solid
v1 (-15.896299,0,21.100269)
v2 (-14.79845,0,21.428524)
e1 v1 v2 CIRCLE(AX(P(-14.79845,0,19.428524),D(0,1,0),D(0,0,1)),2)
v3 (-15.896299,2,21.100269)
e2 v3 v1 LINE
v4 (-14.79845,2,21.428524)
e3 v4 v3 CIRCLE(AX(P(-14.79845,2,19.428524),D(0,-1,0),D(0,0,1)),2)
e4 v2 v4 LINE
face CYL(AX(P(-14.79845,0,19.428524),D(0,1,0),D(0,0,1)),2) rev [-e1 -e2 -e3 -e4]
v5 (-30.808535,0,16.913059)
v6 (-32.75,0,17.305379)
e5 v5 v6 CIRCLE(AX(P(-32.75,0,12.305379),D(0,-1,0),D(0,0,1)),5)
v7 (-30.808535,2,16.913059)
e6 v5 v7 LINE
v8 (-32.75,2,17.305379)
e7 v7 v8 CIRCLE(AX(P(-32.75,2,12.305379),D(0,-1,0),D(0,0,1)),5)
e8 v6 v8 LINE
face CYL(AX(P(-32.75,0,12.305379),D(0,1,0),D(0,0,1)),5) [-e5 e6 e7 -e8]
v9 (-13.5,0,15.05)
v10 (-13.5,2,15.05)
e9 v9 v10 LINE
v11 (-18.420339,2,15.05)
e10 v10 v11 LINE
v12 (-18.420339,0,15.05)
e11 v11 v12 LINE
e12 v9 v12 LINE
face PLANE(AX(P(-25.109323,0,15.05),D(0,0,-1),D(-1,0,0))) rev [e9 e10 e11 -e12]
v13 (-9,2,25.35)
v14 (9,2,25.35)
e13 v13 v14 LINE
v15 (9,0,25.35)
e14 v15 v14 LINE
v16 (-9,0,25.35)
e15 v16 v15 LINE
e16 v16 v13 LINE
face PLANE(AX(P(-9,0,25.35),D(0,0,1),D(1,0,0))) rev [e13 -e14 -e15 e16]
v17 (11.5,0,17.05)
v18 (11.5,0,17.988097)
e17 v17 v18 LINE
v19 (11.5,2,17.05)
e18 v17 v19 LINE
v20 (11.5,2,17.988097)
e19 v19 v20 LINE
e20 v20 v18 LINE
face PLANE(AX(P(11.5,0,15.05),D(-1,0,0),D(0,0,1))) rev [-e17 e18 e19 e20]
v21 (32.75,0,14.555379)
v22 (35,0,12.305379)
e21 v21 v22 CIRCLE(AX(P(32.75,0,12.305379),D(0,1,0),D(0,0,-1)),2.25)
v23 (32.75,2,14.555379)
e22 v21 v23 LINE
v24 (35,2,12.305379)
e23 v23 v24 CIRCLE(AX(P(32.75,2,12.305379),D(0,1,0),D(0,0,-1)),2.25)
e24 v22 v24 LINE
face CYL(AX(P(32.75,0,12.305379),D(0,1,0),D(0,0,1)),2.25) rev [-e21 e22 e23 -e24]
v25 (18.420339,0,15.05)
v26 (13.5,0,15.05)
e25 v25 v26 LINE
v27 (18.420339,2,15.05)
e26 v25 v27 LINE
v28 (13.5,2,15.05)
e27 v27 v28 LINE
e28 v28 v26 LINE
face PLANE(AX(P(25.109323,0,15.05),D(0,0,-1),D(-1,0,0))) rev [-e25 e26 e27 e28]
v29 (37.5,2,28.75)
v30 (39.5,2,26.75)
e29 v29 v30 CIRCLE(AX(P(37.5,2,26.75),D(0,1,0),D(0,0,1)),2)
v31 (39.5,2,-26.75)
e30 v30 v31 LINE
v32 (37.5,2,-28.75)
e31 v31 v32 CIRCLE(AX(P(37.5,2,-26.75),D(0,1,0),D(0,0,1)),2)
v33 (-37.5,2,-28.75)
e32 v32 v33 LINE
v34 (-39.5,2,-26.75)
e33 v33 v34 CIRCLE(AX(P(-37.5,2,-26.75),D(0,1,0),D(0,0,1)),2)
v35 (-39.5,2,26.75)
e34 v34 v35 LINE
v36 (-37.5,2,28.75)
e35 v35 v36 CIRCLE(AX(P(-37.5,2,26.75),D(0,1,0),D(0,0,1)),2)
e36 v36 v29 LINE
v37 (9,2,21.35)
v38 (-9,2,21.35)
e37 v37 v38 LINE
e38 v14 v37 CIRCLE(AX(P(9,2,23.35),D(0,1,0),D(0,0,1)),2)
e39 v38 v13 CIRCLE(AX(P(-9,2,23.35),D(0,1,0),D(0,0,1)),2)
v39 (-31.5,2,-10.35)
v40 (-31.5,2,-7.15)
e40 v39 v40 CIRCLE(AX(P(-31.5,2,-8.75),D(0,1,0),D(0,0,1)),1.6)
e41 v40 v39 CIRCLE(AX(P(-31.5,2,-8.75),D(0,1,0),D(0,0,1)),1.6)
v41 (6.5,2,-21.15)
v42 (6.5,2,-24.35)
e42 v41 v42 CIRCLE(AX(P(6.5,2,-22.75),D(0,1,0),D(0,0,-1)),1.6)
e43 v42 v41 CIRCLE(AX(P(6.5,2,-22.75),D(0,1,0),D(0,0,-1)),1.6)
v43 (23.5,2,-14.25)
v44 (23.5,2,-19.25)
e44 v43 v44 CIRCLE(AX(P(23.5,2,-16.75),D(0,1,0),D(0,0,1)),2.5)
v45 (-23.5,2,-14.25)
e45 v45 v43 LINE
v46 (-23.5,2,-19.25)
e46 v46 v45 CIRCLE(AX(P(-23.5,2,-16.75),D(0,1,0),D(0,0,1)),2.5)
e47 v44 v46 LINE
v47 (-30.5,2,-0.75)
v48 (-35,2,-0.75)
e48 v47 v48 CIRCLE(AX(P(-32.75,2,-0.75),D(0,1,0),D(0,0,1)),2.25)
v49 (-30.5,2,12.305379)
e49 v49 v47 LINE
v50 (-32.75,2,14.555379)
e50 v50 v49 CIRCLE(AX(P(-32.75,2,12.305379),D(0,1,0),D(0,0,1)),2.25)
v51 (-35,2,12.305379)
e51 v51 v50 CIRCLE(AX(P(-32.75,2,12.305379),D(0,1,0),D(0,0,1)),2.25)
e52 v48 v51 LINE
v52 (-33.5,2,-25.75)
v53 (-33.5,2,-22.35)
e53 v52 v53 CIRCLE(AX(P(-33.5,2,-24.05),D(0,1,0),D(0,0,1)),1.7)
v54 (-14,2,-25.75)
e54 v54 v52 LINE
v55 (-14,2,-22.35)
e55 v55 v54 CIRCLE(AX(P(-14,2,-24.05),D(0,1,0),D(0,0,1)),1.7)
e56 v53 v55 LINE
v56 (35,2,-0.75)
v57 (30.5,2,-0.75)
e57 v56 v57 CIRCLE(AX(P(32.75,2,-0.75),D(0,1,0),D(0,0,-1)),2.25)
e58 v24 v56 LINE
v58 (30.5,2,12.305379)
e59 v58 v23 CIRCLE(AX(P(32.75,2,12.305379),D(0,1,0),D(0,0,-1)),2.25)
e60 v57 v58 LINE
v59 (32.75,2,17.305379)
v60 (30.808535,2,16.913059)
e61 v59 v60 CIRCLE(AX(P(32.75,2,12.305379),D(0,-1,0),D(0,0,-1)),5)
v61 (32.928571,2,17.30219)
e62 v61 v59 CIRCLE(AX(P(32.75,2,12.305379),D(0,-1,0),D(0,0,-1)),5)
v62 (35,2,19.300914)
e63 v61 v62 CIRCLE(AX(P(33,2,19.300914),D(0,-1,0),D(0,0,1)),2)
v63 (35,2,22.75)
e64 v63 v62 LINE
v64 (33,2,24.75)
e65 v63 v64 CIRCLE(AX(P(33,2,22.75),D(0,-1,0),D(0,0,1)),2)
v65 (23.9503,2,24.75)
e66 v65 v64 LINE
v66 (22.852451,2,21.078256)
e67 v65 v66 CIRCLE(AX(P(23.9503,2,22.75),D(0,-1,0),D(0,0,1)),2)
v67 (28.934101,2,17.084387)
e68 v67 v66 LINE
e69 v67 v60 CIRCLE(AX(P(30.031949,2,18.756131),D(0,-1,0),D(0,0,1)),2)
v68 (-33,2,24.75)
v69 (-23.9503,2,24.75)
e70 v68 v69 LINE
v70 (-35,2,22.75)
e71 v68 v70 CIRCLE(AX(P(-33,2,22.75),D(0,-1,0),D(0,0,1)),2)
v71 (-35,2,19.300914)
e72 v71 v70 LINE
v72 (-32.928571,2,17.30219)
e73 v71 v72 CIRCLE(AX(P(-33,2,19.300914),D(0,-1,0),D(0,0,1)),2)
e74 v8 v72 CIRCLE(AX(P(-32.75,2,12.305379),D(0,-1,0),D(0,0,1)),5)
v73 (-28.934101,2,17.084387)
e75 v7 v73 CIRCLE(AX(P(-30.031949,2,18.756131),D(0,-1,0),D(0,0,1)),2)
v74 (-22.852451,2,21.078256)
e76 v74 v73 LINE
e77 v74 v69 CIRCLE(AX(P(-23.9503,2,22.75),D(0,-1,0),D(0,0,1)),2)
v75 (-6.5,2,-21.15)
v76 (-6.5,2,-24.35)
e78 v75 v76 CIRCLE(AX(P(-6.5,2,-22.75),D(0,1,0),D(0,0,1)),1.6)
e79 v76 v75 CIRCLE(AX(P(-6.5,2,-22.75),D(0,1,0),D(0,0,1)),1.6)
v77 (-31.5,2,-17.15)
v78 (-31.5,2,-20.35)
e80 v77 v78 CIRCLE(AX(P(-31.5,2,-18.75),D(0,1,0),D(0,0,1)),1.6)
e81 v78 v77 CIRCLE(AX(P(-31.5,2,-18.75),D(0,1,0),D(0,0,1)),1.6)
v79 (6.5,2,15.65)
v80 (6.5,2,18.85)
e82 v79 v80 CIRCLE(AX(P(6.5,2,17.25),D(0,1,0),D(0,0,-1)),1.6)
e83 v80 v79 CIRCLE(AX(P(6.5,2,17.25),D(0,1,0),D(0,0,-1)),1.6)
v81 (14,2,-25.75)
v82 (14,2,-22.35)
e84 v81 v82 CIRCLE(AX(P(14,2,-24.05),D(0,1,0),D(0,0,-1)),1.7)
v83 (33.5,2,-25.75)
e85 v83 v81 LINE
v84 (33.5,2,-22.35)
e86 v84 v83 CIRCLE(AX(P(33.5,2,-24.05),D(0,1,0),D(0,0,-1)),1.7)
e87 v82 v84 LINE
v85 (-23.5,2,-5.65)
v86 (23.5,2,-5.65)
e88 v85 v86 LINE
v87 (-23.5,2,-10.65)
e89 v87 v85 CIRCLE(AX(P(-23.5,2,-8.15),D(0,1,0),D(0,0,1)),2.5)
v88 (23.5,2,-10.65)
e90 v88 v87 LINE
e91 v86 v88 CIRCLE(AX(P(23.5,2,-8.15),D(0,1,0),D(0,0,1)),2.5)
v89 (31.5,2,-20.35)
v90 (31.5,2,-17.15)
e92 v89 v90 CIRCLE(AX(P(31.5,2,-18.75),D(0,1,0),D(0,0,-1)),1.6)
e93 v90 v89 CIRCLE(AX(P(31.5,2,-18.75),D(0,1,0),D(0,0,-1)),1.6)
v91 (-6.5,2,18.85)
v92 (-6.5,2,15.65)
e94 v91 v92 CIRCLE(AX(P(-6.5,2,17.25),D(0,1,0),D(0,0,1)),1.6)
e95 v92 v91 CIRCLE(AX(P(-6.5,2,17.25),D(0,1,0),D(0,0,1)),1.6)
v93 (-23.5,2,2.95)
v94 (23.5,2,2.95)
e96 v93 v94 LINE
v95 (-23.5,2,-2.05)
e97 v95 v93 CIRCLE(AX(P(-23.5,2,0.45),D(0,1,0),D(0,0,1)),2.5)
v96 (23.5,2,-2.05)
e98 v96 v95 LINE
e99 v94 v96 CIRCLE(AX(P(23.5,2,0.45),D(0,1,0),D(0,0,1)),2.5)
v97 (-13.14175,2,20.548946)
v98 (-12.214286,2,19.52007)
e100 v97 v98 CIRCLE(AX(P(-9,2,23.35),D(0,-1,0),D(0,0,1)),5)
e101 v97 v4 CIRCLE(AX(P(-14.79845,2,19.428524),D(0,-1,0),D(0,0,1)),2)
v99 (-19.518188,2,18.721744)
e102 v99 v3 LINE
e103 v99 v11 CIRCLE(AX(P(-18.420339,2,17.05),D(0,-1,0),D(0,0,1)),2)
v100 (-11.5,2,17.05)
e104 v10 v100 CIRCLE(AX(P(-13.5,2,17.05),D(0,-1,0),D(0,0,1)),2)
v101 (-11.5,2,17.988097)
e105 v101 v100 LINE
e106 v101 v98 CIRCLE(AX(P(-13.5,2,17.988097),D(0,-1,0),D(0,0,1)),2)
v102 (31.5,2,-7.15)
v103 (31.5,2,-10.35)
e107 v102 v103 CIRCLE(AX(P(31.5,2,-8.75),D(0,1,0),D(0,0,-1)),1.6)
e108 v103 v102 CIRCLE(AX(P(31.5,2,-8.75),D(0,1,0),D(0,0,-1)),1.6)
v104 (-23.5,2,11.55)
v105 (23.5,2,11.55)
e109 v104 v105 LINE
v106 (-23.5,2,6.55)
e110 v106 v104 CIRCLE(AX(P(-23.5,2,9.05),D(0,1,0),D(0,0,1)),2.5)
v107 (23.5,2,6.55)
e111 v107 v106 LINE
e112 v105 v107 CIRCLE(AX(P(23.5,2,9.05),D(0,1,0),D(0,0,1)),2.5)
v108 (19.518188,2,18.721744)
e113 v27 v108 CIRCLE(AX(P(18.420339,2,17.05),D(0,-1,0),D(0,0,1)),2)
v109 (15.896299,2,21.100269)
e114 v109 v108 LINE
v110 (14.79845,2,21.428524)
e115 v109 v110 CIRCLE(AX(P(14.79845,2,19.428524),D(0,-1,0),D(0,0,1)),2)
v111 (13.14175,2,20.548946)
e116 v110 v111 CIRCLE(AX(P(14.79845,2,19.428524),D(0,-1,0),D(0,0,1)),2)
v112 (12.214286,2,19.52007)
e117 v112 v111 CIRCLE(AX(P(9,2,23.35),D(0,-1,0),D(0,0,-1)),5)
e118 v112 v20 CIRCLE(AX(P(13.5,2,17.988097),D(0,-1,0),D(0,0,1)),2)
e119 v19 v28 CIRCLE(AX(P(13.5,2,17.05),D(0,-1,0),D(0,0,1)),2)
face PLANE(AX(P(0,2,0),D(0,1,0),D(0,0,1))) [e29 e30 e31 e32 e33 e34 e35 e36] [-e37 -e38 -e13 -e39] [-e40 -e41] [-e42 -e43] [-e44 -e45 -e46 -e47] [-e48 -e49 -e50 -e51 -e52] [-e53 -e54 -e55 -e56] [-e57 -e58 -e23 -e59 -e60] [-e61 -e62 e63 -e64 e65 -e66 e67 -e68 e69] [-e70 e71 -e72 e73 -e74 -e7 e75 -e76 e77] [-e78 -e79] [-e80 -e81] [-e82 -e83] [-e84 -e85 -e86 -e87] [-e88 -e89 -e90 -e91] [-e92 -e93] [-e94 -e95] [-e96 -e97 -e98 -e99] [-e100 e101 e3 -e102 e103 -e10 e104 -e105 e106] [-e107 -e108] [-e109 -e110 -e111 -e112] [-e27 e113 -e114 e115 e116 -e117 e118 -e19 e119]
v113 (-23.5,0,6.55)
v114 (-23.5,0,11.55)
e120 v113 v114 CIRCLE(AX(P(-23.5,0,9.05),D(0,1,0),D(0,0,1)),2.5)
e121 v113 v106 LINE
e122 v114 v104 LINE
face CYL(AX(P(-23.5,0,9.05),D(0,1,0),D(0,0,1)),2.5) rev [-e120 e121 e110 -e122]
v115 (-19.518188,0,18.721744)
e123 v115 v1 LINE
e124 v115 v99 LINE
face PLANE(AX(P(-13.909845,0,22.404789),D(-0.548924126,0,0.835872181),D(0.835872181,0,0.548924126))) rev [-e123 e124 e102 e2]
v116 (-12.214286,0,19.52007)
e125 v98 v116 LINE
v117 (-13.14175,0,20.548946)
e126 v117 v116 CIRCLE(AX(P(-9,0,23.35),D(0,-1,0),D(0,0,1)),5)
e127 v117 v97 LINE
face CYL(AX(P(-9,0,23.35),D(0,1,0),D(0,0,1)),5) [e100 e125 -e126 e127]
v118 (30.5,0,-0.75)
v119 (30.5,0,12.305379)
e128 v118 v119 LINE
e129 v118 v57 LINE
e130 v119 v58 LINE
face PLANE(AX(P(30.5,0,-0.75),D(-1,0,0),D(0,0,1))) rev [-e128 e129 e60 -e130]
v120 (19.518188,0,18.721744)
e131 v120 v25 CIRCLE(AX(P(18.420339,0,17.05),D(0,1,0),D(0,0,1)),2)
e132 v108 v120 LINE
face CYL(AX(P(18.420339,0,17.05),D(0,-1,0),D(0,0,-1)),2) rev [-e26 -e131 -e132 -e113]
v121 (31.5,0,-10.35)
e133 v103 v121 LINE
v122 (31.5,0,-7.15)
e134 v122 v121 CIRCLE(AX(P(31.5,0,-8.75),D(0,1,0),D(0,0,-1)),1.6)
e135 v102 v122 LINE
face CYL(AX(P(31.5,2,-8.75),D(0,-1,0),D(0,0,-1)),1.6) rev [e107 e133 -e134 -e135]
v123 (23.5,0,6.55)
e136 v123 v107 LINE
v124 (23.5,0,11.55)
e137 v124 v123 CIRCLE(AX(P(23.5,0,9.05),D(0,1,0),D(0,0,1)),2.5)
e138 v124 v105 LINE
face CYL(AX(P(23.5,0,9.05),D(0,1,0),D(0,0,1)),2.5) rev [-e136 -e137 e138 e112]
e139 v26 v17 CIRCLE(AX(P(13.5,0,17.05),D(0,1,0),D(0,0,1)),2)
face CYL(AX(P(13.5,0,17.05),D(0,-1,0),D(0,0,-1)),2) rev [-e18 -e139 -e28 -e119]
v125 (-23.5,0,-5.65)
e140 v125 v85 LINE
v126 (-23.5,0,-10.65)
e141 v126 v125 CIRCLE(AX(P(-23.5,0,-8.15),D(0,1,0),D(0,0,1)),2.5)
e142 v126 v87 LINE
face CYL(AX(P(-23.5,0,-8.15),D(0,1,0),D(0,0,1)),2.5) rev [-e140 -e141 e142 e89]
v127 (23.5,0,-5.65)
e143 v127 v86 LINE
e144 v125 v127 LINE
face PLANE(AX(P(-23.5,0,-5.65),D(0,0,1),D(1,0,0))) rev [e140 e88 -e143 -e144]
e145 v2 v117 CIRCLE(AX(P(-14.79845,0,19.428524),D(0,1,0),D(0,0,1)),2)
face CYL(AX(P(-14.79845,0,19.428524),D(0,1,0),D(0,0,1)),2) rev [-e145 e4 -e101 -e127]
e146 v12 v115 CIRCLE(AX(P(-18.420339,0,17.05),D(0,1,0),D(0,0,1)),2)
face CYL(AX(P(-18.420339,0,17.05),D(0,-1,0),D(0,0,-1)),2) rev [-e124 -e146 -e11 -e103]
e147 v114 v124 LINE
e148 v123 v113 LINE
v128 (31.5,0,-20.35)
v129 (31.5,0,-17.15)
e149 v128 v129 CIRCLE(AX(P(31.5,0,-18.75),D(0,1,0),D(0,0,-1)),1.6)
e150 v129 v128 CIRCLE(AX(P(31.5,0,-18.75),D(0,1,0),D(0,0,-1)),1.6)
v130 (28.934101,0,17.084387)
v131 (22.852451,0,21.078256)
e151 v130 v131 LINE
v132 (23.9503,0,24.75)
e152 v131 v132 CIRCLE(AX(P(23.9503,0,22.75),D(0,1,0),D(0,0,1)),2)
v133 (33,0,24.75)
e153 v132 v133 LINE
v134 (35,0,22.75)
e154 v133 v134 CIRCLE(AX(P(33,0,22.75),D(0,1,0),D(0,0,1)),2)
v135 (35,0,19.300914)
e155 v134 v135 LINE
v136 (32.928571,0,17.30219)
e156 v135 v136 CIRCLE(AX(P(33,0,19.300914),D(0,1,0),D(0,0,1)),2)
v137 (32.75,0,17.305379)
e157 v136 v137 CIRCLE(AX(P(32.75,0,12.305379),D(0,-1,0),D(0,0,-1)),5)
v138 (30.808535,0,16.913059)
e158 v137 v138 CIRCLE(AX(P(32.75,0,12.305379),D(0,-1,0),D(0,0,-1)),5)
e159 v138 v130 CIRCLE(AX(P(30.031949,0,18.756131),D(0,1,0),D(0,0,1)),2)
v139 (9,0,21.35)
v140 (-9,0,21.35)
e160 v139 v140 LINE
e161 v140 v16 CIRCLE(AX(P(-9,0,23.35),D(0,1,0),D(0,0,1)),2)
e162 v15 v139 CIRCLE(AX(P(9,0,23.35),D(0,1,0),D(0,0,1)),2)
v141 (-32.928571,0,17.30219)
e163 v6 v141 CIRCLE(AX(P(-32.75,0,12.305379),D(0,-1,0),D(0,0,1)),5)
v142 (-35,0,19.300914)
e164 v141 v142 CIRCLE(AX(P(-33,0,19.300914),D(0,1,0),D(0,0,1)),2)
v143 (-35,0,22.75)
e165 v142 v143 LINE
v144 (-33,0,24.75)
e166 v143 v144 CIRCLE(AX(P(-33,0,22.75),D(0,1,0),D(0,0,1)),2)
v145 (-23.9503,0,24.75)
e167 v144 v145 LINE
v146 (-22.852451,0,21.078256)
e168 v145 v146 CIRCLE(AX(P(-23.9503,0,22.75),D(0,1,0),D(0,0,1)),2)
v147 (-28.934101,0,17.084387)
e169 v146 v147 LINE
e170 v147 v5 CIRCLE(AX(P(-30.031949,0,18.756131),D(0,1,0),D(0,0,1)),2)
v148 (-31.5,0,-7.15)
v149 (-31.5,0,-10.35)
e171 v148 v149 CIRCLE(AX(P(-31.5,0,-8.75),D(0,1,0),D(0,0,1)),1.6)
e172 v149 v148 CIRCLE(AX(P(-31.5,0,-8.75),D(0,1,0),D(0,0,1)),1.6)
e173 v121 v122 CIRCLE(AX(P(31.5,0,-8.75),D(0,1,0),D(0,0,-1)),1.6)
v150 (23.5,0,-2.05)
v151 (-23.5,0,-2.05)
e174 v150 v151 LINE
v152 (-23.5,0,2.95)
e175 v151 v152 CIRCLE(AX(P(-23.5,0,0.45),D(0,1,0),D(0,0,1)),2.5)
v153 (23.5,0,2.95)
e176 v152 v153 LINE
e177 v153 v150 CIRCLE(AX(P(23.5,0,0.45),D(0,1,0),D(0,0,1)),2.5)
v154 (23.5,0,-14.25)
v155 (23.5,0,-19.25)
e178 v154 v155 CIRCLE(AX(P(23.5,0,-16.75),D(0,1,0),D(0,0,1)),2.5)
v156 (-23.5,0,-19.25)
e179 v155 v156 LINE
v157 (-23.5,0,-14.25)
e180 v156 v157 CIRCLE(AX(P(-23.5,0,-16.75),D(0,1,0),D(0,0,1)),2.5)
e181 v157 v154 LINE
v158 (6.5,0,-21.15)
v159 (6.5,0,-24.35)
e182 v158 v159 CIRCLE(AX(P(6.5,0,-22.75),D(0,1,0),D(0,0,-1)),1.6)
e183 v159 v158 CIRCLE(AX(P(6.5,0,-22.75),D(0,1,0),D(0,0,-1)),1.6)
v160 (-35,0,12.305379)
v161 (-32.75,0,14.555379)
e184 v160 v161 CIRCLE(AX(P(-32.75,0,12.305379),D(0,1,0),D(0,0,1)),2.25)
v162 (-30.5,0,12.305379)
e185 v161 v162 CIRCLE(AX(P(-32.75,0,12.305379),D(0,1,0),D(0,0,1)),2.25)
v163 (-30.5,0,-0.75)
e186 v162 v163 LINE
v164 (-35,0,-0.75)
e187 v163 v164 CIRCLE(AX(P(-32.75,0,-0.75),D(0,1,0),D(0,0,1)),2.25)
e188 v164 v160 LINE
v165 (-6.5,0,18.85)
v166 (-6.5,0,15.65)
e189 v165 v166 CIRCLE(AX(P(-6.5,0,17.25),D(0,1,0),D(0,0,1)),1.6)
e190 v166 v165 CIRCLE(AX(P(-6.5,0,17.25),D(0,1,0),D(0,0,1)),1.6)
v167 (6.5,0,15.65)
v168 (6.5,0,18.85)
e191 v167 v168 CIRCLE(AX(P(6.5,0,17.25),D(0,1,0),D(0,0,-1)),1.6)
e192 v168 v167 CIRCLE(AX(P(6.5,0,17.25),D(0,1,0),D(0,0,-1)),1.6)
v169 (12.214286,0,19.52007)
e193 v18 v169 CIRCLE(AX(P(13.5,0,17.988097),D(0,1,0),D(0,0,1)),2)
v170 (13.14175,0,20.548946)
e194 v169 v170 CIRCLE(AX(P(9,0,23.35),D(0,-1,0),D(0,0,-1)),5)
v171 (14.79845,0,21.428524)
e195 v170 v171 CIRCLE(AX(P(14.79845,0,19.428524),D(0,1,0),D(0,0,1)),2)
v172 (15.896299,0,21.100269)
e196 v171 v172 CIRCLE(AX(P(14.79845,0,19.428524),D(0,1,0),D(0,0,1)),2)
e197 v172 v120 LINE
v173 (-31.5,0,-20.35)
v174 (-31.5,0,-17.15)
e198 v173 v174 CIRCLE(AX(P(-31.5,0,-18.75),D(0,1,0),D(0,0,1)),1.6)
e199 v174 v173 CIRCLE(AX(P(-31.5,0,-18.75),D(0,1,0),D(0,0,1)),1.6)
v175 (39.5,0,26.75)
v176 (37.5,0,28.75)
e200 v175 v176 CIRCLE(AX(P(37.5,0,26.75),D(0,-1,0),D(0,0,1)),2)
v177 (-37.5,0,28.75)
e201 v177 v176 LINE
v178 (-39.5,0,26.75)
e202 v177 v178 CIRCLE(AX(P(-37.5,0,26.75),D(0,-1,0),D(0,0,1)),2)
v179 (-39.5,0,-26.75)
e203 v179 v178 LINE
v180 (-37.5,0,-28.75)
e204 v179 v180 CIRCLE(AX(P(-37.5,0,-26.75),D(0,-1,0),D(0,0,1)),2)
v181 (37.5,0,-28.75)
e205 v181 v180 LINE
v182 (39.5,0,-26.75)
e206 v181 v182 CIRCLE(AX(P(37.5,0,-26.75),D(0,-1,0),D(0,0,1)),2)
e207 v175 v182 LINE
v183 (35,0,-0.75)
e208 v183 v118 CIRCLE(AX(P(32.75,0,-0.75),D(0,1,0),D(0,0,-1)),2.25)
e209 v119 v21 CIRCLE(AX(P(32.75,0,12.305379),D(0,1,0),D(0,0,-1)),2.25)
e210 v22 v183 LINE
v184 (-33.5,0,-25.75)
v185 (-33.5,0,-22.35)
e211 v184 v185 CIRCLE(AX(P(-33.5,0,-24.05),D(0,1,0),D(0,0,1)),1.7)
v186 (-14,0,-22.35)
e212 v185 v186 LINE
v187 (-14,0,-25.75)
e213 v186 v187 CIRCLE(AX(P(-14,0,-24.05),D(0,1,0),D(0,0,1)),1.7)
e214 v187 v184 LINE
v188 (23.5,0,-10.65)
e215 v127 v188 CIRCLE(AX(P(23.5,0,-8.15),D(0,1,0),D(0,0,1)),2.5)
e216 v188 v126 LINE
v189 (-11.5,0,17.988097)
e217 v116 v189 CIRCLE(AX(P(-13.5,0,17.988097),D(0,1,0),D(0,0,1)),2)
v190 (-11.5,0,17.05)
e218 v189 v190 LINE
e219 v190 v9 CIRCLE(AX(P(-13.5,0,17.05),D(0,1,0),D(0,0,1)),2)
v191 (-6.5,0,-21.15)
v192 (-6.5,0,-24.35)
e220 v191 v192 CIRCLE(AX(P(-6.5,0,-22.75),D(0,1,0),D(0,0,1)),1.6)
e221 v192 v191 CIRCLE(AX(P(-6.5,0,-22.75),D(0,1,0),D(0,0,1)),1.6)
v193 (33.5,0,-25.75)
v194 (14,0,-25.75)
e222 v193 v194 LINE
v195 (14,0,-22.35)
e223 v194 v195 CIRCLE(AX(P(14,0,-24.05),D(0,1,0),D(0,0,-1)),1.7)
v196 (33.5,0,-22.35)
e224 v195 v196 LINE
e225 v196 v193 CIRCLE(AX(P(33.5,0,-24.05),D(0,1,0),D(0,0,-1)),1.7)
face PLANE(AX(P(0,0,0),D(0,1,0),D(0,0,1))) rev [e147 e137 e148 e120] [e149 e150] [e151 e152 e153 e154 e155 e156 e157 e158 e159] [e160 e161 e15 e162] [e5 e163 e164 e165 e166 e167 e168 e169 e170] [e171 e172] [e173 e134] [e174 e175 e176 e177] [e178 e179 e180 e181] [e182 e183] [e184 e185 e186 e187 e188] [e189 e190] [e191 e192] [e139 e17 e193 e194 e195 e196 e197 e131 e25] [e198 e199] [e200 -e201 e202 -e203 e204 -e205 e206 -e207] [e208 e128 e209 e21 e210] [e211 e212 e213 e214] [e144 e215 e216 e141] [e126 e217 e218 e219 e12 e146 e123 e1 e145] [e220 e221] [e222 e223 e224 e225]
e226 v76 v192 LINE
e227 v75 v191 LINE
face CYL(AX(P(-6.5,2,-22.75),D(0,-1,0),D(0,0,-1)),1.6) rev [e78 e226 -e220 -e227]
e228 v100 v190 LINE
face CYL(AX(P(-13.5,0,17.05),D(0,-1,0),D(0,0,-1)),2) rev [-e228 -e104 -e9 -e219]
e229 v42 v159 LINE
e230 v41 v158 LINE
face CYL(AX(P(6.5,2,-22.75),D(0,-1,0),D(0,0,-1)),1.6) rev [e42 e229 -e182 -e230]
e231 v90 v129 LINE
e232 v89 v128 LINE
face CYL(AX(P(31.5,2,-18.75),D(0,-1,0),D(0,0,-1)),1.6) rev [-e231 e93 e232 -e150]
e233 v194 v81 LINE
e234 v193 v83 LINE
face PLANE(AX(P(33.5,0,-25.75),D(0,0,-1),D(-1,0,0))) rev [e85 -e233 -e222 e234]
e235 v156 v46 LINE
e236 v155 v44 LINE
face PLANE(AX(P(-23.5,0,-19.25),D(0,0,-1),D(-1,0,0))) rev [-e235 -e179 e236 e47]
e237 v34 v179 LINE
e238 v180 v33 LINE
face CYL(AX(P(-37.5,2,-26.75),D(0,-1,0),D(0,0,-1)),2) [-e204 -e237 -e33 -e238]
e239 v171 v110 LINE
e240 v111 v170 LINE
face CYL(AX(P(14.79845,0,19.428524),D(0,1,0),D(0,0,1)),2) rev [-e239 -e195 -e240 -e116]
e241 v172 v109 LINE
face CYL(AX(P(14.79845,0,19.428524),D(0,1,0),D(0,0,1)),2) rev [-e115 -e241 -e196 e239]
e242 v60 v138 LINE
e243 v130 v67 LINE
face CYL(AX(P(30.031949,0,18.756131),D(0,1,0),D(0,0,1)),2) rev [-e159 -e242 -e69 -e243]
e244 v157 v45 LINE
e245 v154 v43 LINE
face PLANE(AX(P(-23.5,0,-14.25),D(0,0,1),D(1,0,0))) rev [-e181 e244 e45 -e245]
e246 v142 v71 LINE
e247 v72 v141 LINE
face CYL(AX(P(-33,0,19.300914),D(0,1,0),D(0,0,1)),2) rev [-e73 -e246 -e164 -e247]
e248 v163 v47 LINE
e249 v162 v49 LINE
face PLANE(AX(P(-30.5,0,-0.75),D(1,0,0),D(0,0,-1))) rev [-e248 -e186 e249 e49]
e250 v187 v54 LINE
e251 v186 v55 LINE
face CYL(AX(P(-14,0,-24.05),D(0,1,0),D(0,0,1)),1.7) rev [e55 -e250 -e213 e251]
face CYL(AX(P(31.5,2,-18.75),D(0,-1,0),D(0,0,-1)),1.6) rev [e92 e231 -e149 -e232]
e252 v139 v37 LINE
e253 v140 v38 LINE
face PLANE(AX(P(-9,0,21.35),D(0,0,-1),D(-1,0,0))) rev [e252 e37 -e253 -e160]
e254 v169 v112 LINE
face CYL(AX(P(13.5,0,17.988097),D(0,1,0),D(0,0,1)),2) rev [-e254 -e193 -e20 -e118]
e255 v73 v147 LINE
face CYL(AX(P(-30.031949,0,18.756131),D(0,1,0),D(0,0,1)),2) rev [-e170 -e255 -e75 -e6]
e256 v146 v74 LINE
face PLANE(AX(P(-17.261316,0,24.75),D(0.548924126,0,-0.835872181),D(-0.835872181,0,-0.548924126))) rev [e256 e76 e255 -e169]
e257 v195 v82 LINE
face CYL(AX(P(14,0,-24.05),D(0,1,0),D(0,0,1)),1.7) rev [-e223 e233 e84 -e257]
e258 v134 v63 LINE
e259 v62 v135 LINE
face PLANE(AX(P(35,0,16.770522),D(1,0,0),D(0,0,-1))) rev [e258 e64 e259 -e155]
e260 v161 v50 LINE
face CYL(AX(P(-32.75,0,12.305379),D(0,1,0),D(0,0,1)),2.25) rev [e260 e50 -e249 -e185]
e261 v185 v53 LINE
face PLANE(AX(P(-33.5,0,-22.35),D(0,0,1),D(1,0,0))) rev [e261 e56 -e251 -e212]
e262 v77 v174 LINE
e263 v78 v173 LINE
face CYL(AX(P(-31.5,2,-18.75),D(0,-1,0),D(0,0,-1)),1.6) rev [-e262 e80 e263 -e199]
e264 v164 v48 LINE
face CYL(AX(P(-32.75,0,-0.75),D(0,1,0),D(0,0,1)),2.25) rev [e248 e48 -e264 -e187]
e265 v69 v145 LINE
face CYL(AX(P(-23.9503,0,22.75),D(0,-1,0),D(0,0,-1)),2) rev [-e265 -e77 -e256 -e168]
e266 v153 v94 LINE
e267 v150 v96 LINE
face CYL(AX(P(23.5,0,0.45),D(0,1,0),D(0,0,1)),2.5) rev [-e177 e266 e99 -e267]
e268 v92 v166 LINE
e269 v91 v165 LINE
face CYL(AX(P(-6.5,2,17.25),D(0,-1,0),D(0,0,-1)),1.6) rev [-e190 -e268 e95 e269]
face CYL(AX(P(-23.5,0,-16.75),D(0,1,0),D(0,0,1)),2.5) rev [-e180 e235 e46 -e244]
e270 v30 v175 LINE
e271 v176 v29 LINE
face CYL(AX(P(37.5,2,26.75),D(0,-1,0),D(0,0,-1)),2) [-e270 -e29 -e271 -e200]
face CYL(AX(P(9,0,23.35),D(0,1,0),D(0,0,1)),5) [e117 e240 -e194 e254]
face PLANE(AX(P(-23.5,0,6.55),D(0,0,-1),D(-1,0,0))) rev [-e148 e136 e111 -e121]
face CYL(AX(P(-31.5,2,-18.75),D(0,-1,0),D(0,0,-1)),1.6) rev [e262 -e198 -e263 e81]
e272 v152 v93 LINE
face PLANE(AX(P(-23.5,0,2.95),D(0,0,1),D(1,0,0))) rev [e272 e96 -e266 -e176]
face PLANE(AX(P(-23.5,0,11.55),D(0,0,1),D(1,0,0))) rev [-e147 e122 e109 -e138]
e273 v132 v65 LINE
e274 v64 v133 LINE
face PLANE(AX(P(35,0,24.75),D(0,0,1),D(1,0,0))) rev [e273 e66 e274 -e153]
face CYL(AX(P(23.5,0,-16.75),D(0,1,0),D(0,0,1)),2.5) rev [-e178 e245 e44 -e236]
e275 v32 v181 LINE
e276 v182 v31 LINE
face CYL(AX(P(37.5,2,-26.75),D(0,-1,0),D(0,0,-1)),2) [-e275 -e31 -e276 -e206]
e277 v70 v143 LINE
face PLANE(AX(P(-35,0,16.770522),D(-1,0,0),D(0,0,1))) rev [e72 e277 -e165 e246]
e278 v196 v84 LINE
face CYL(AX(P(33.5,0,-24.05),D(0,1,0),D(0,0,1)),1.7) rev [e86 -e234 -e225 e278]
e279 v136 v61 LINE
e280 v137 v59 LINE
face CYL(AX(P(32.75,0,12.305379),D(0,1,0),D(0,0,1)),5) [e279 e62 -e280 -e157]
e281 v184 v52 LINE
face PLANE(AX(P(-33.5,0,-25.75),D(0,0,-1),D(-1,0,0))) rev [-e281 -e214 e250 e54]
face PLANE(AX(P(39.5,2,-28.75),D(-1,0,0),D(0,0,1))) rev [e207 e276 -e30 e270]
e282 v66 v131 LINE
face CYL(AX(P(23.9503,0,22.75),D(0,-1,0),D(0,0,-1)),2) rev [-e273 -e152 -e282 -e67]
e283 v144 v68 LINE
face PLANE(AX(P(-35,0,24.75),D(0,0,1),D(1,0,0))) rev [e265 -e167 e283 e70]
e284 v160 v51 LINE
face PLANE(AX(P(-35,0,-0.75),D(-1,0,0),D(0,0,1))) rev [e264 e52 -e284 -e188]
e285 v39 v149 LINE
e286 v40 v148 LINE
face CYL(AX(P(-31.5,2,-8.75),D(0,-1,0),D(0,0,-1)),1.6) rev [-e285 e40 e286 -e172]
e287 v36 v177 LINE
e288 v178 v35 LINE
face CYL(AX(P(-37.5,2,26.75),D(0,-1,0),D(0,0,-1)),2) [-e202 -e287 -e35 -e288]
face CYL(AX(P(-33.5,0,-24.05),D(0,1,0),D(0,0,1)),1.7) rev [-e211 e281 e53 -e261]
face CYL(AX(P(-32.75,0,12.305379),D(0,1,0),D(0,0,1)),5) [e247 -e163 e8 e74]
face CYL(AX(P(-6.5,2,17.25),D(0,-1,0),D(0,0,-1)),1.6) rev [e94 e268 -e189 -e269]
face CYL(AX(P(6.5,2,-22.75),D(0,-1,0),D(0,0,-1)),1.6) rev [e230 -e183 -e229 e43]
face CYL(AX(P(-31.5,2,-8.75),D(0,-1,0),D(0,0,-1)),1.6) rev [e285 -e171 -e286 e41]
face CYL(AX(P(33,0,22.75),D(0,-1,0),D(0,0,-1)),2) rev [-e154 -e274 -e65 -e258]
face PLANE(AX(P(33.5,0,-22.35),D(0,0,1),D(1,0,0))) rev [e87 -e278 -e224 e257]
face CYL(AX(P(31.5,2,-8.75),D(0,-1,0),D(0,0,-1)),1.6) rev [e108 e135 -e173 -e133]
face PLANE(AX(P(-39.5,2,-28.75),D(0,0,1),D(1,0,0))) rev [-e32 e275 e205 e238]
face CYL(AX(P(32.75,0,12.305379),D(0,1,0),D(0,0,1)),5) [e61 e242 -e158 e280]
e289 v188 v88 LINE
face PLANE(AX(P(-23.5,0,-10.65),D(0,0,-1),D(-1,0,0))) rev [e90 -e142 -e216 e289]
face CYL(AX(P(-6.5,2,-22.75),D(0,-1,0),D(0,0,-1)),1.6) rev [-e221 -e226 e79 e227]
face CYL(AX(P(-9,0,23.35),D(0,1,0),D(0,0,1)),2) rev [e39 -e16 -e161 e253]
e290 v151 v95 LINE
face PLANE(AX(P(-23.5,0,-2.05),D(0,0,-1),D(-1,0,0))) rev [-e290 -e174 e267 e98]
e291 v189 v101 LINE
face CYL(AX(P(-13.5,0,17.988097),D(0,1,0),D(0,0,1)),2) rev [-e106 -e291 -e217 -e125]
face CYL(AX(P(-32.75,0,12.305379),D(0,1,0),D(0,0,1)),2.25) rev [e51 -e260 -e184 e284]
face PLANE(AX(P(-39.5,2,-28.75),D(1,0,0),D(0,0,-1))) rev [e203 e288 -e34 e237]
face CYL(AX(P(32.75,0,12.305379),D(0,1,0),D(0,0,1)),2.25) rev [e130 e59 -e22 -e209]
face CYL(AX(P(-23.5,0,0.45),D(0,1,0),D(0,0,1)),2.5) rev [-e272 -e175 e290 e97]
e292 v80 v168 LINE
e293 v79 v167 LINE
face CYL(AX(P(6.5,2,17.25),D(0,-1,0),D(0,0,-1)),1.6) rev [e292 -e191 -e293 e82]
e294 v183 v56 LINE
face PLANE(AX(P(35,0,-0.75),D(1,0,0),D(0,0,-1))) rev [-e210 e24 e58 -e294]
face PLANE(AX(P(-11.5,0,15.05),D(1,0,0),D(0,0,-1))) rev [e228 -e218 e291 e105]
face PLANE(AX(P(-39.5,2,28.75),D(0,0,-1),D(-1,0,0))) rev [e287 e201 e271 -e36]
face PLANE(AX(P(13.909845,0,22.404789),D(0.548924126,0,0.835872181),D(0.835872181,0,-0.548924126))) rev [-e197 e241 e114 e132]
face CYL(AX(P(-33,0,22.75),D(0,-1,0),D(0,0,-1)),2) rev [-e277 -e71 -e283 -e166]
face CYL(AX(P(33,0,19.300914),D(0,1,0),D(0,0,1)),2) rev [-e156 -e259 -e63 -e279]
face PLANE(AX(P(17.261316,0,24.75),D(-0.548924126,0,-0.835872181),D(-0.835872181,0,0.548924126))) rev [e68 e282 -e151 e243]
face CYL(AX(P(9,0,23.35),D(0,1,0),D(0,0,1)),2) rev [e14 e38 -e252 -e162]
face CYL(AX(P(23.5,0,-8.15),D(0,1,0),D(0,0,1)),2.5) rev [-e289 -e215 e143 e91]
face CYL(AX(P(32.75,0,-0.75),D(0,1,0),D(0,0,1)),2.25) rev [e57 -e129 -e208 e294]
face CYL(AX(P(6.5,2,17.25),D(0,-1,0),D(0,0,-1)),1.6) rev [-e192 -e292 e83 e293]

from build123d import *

# Parameters (mm, degrees)
SKETCH_1_W          = 79
SKETCH_1_H          = 57.5
SKETCH_1_R          = 1.6
EXTRUDE_1_DEPTH     = 2
CUT_EXTRUDE_1_DEPTH = 49.895935414
FILLET_R2_1_R       = 2


with BuildPart() as part:
    # 草图1 → 凸台-拉伸1 (new body)
    with BuildSketch(Plane(origin=(0, 0, 0), x_dir=(1, 0, 0), z_dir=(0, 1, 0))):
        Rectangle(SKETCH_1_W, SKETCH_1_H)
        with Locations(Location((-31.5, 18.75, 0), (0, 0, 270))):
            Circle(SKETCH_1_R, mode=Mode.SUBTRACT)
        with Locations(Location((-31.5, 8.75, 0), (0, 0, 270))):
            Circle(SKETCH_1_R, mode=Mode.SUBTRACT)
        with Locations(Location((31.5, 8.75, 0), (0, 0, 90))):
            Circle(SKETCH_1_R, mode=Mode.SUBTRACT)
        with Locations(Location((31.5, 18.75, 0), (0, 0, 90))):
            Circle(SKETCH_1_R, mode=Mode.SUBTRACT)
        with Locations(Location((-6.5, 22.75, 0), (0, 0, 270))):
            Circle(SKETCH_1_R, mode=Mode.SUBTRACT)
        with Locations(Location((-6.5, -17.25, 0), (0, 0, 270))):
            Circle(SKETCH_1_R, mode=Mode.SUBTRACT)
        with Locations(Location((6.5, 22.75, 0), (0, 0, 90))):
            Circle(SKETCH_1_R, mode=Mode.SUBTRACT)
        with Locations(Location((6.5, -17.25, 0), (0, 0, 90))):
            Circle(SKETCH_1_R, mode=Mode.SUBTRACT)
    extrude(amount=EXTRUDE_1_DEPTH)

    # 草图2 → 切除-拉伸1 (cut, through all)
    with BuildSketch(Plane(origin=(0, 2, 0), x_dir=(1, 0, 0), z_dir=(0, 1, 0))):
        with BuildLine():
            Line((-23.5, 19.25), (23.5, 19.25))
            ThreePointArc((23.5, 19.25), (26, 16.75), (23.5, 14.25))
            Line((23.5, 14.25), (-23.5, 14.25))
            ThreePointArc((-23.5, 14.25), (-26, 16.75), (-23.5, 19.25))
        make_face()
        with BuildLine():
            Line((-23.5, 10.65), (23.5, 10.65))
            ThreePointArc((23.5, 10.65), (26, 8.15), (23.5, 5.65))
            Line((23.5, 5.65), (-23.5, 5.65))
            ThreePointArc((-23.5, 5.65), (-26, 8.15), (-23.5, 10.65))
        make_face()
        with BuildLine():
            Line((-23.5, 2.05), (23.5, 2.05))
            ThreePointArc((23.5, 2.05), (26, -0.45), (23.5, -2.95))
            Line((23.5, -2.95), (-23.5, -2.95))
            ThreePointArc((-23.5, -2.95), (-26, -0.45), (-23.5, 2.05))
        make_face()
        with BuildLine():
            Line((-23.5, -6.55), (23.5, -6.55))
            ThreePointArc((23.5, -6.55), (26, -9.05), (23.5, -11.55))
            Line((23.5, -11.55), (-23.5, -11.55))
            ThreePointArc((-23.5, -11.55), (-26, -9.05), (-23.5, -6.55))
        make_face()
        with BuildLine():
            Line((-33.5, 25.75), (-14, 25.75))
            ThreePointArc((-14, 25.75), (-12.3, 24.05), (-14, 22.35))
            Line((-14, 22.35), (-33.5, 22.35))
            ThreePointArc((-33.5, 22.35), (-35.2, 24.05), (-33.5, 25.75))
        make_face()
        with BuildLine():
            Line((33.5, 25.75), (14, 25.75))
            ThreePointArc((14, 25.75), (12.3, 24.05), (14, 22.35))
            Line((14, 22.35), (33.5, 22.35))
            ThreePointArc((33.5, 22.35), (35.2, 24.05), (33.5, 25.75))
        make_face()
        with BuildLine():
            Line((-9, -21.35), (9, -21.35))
            ThreePointArc((9, -21.35), (11, -23.35), (9, -25.35))
            Line((9, -25.35), (-9, -25.35))
            ThreePointArc((-9, -25.35), (-11, -23.35), (-9, -21.35))
        make_face()
        with BuildLine():
            Line((-30.5, 0.75), (-30.5, -12.305379368))
            ThreePointArc((-30.5, -12.305379368), (-32.75, -14.555379368), (-35, -12.305379368))
            Line((-35, -12.305379368), (-35, 0.75))
            ThreePointArc((-35, 0.75), (-32.75, 3), (-30.5, 0.75))
        make_face()
        with BuildLine():
            Line((30.5, 0.75), (30.5, -12.305379368))
            ThreePointArc((30.5, -12.305379368), (32.75, -14.555379368), (35, -12.305379368))
            Line((35, -12.305379368), (35, 0.75))
            ThreePointArc((35, 0.75), (32.75, 3), (30.5, 0.75))
        make_face()
        with BuildLine():
            Line((-35, -16.770522143), (-35, -24.75))
            Line((-35, -24.75), (-17.261316253, -24.75))
            Line((-17.261316253, -24.75), (-29.927103479, -16.432273507))
            ThreePointArc((-29.927103479, -16.432273507), (-32.417350574, -17.294301533), (-35, -16.770522143))
        make_face()
        with BuildLine():
            Line((-25.10932284, -15.05), (-11.5, -15.05))
            Line((-11.5, -15.05), (-11.5, -19.019872981))
            ThreePointArc((-11.5, -19.019872981), (-13.073188505, -20.450149072), (-13.909844854, -22.404789172))
            Line((-13.909844854, -22.404789172), (-25.10932284, -15.05))
        make_face()
        with BuildLine():
            Line((17.261316253, -24.75), (29.927103479, -16.432273507))
            ThreePointArc((29.927103479, -16.432273507), (32.417350574, -17.294301533), (35, -16.770522143))
            Line((35, -16.770522143), (35, -24.75))
            Line((35, -24.75), (17.261316253, -24.75))
        make_face()
        with BuildLine():
            Line((25.10932284, -15.05), (11.5, -15.05))
            Line((11.5, -15.05), (11.5, -19.019872981))
            ThreePointArc((11.5, -19.019872981), (13.073188505, -20.450149072), (13.909844854, -22.404789172))
            Line((13.909844854, -22.404789172), (25.10932284, -15.05))
        make_face()
    extrude(amount=-CUT_EXTRUDE_1_DEPTH, mode=Mode.SUBTRACT)

    # R2 圆角1
    fillet_r2_1_edges = [part.edges().sort_by_distance(p)[0] for p in [
        (-11.5, 1, 15.05),
        (-11.5, 1, 19.019872981),
        (-13.909844854, 1, 22.404789172),
        (-25.10932284, 1, 15.05),
        (-35, 1, 16.770522143),
        (-29.927103479, 1, 16.432273507),
        (-17.261316253, 1, 24.75),
        (-35, 1, 24.75),
        (25.10932284, 1, 15.05),
        (13.909844854, 1, 22.404789172),
        (11.5, 1, 19.019872981),
        (11.5, 1, 15.05),
        (29.927103479, 1, 16.432273507),
        (35, 1, 16.770522143),
        (35, 1, 24.75),
        (17.261316253, 1, 24.75),
        (39.5, 1, 28.75),
        (-39.5, 1, 28.75),
        (-39.5, 1, -28.75),
        (39.5, 1, -28.75),
    ]]
    fillet(fillet_r2_1_edges, radius=FILLET_R2_1_R)


solid = part.part
